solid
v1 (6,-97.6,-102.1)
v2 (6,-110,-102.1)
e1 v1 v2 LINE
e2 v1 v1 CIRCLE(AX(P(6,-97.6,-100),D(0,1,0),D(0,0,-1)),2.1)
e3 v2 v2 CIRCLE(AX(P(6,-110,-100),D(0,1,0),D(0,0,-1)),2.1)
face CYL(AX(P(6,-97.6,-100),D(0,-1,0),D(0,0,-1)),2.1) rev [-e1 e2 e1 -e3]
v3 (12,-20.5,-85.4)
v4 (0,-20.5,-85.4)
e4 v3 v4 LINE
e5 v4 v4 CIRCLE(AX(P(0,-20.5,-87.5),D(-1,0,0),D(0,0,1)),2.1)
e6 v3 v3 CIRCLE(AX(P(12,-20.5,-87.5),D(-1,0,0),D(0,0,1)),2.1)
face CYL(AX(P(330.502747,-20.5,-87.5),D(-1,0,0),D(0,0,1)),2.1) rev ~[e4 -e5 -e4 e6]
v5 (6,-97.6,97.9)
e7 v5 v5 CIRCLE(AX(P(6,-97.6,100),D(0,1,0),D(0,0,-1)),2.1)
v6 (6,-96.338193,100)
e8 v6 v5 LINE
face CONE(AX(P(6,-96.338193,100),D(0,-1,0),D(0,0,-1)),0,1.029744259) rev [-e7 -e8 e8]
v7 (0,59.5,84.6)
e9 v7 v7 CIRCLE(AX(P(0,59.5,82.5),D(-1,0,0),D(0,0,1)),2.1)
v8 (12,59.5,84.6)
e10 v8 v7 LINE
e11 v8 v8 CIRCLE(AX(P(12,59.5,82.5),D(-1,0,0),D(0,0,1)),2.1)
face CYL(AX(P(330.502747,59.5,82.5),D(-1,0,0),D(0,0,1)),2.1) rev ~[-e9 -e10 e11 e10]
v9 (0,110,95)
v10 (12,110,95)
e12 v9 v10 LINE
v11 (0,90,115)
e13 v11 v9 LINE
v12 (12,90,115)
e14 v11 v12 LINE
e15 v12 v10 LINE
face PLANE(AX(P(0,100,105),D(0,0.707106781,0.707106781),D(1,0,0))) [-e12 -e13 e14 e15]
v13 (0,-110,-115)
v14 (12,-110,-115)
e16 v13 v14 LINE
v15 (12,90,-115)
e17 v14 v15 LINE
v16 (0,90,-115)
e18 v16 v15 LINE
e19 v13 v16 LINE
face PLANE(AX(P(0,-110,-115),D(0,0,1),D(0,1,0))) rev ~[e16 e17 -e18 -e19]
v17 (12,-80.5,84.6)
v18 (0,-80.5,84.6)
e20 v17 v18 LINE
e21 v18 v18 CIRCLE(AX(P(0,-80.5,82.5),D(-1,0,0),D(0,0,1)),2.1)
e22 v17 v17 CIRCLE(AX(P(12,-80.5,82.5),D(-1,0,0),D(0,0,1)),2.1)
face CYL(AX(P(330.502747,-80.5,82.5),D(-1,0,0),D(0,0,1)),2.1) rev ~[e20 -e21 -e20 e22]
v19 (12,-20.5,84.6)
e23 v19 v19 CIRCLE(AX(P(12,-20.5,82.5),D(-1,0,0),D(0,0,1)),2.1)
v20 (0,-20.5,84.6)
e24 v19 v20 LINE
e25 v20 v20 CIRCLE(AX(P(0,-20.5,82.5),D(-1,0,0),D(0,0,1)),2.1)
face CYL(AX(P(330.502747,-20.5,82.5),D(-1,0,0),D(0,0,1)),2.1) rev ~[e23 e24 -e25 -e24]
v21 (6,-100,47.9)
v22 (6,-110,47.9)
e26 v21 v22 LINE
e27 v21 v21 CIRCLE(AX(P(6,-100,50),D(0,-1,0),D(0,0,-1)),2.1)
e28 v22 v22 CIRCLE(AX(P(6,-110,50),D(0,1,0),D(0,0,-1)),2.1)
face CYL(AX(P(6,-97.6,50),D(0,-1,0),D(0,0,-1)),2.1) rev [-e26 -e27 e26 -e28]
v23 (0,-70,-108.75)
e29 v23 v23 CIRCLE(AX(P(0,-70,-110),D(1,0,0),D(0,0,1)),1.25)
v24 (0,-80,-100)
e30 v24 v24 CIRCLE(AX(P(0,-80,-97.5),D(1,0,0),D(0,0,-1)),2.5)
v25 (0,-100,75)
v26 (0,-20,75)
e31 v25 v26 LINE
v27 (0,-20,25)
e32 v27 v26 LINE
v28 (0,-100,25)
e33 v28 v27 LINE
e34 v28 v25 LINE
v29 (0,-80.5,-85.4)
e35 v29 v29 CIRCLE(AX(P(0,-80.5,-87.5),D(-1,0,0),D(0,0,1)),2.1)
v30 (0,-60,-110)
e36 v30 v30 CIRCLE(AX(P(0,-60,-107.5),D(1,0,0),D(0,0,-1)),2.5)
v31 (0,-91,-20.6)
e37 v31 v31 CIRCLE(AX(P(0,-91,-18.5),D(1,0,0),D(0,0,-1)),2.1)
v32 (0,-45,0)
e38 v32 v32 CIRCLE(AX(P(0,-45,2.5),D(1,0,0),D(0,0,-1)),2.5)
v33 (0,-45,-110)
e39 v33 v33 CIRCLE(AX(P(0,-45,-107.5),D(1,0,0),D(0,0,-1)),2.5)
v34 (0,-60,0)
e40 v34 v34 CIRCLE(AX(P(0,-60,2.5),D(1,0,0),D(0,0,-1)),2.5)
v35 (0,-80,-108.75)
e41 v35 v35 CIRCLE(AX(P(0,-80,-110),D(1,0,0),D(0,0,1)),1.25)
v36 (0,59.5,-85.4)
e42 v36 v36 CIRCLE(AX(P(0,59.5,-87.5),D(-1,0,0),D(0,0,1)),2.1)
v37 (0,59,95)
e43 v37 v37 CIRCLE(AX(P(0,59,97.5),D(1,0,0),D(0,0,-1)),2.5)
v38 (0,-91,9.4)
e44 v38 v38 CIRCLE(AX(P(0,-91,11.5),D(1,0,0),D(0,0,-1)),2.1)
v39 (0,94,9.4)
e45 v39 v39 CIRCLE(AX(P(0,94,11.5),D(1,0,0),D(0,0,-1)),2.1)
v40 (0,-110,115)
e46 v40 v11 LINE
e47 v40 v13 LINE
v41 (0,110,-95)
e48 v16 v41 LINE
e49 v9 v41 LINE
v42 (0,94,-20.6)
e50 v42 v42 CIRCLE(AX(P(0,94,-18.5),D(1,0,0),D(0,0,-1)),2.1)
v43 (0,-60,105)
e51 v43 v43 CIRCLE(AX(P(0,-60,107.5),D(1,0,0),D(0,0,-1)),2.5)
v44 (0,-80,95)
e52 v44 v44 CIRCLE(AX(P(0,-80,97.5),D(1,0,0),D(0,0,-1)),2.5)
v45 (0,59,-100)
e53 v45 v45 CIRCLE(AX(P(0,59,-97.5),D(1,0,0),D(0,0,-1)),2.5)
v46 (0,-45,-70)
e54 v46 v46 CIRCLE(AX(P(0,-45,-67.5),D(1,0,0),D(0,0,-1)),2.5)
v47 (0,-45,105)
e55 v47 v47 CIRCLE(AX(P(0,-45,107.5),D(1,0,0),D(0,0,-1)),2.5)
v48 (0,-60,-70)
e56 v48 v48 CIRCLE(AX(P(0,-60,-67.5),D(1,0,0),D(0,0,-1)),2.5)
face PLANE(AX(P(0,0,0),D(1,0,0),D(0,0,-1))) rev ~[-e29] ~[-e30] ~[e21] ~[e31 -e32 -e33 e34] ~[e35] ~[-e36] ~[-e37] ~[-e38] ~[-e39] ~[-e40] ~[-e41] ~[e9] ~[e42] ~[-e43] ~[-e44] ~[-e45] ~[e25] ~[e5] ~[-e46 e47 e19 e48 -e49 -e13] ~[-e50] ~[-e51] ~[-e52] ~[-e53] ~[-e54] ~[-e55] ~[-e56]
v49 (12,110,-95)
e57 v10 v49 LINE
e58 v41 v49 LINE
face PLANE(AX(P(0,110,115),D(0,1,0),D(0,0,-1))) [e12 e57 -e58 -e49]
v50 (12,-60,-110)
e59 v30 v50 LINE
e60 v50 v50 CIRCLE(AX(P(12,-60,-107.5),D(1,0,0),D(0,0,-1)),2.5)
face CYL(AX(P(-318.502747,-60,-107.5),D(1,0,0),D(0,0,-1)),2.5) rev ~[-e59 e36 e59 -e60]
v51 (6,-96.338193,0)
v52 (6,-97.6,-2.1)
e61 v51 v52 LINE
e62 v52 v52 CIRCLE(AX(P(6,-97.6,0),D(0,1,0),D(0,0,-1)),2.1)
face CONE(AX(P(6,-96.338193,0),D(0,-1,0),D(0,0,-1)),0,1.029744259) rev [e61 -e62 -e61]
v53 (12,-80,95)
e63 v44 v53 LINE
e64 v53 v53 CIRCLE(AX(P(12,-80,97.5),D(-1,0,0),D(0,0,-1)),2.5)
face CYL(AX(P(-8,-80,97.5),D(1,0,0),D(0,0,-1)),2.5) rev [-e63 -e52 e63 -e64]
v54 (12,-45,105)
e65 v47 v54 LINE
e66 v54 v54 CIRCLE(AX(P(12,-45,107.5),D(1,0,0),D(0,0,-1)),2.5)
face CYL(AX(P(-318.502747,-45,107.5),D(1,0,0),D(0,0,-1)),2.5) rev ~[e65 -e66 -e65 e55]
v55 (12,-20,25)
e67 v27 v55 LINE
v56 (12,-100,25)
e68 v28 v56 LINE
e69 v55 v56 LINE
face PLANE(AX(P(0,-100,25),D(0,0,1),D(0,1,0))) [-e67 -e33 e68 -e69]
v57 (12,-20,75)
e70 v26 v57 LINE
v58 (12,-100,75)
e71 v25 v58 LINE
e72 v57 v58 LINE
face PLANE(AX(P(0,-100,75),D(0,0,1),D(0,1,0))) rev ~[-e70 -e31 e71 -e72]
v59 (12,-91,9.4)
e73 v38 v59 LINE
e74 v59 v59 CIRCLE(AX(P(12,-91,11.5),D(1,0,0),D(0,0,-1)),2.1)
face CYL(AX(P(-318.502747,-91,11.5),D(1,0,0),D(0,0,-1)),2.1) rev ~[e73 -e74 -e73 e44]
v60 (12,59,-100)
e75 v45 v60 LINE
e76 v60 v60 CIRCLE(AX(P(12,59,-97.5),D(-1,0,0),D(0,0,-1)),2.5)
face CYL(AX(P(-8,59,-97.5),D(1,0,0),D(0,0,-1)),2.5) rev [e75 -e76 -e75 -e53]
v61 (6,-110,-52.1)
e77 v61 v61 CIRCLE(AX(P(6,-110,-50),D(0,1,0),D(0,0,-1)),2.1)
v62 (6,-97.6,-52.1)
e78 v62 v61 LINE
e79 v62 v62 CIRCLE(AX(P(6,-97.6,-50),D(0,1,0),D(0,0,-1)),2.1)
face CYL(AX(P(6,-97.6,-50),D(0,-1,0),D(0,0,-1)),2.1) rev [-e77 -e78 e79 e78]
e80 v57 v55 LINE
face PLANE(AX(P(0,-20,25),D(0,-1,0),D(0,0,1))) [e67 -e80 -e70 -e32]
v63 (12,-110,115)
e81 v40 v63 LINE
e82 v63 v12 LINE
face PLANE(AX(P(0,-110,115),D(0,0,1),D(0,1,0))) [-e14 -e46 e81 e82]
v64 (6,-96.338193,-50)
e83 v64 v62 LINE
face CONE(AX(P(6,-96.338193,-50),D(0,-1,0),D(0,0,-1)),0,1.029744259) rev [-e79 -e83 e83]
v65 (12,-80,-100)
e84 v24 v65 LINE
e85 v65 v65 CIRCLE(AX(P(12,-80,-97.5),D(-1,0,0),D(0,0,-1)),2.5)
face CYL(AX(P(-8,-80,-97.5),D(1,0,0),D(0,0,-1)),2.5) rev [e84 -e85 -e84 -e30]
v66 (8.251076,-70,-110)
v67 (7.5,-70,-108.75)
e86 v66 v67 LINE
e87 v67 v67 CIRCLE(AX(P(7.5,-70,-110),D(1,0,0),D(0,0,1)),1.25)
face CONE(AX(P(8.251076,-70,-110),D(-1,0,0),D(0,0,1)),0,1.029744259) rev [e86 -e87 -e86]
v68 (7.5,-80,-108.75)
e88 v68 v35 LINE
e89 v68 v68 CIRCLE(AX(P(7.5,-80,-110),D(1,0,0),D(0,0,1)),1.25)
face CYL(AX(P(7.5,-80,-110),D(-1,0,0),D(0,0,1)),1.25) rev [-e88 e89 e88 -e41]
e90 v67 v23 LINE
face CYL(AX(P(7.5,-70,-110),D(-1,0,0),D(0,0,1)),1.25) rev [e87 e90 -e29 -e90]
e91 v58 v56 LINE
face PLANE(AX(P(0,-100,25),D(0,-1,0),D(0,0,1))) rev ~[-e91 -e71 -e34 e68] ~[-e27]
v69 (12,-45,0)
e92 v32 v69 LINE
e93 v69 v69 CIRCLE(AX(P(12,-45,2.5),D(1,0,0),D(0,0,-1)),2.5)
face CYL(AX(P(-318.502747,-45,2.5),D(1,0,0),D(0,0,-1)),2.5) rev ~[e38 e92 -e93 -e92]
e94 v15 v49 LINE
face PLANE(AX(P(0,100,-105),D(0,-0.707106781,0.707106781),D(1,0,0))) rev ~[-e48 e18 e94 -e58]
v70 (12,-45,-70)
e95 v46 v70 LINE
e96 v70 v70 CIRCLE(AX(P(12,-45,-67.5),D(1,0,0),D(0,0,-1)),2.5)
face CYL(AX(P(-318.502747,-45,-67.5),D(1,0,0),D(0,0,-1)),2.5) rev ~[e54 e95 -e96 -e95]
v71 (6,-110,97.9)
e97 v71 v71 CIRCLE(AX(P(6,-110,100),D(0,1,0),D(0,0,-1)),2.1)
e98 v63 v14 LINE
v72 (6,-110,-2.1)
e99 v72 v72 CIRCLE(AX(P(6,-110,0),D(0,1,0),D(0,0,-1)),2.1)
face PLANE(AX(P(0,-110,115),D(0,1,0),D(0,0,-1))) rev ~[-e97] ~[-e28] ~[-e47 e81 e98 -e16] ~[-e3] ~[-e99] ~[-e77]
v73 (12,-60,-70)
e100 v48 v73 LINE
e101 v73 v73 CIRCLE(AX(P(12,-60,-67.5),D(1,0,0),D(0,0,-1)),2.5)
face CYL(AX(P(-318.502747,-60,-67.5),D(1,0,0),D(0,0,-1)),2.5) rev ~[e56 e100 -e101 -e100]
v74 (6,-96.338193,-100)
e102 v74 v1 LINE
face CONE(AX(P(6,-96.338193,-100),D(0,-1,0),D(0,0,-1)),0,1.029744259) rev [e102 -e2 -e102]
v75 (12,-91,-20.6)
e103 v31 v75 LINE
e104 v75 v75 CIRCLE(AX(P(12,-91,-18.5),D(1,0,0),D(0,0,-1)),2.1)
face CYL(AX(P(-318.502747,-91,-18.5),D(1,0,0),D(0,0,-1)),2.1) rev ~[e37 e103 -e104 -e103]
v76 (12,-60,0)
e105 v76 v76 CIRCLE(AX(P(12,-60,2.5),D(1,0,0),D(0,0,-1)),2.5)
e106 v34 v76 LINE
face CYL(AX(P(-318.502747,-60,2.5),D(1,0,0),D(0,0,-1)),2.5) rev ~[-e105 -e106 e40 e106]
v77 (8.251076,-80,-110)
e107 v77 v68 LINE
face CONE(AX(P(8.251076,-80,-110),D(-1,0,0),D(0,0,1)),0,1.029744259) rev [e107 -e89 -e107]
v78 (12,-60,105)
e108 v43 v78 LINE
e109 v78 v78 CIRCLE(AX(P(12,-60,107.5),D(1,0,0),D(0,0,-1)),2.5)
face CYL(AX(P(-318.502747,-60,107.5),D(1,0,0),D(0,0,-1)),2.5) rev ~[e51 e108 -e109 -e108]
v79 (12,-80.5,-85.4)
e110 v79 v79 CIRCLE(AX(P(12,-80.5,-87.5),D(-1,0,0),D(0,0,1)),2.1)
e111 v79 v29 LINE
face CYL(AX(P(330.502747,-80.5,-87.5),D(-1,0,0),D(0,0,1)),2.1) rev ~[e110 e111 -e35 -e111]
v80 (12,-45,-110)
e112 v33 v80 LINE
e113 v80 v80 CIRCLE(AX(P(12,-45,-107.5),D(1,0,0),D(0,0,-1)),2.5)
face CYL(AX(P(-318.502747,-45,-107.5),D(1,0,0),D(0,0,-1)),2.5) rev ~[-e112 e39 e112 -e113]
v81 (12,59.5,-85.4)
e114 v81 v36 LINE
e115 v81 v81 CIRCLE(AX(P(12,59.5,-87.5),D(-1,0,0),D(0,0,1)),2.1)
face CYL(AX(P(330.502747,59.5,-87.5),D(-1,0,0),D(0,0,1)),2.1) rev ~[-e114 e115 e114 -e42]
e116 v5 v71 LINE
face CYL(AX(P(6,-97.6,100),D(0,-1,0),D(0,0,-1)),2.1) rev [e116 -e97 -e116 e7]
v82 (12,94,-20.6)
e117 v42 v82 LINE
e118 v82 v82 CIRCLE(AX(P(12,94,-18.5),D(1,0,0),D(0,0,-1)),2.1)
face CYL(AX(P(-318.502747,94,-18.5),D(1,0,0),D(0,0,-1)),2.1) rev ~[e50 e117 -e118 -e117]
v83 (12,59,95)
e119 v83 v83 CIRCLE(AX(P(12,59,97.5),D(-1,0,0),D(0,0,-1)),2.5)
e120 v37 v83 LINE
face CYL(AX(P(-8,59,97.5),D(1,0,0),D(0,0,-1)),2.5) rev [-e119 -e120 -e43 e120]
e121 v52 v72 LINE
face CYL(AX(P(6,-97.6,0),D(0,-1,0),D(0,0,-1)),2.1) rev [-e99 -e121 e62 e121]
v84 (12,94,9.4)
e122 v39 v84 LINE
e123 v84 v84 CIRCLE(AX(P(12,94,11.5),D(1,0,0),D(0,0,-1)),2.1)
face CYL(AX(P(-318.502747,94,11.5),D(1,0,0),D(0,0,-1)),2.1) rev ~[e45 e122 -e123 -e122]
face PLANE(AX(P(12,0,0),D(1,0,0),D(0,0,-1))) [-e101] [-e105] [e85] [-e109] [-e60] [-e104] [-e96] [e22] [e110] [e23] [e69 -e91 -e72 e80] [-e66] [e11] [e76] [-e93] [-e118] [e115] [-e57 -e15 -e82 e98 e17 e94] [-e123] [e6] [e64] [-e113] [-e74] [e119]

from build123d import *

# Parameters (mm, degrees)
SKETCH_1_W                  = 230
SKETCH_1_H                  = 220
BOSS_EXTRUDE_1_DEPTH        = 12
CHAMFER_1_SIZE              = 20
SKETCH_11_W                 = 50
SKETCH_11_H                 = 80
CUT_EXTRUDE_1_DEPTH         = 160.590099944
M6_TAPPED_HOLE_1_D          = 5
LINEAR_PATTERN_4_COUNT      = 2
LINEAR_PATTERN_4_PITCH      = 15
LINEAR_PATTERN_5_COUNT      = 3
LINEAR_PATTERN_5_PITCH      = 50
LINEAR_PATTERN_5_COL_COUNT  = 3
LINEAR_PATTERN_5_COL_PITCH  = 50
LINEAR_PATTERN_6_COUNT      = 2
LINEAR_PATTERN_6_PITCH      = 110
LINEAR_PATTERN_6_COPY_1_D   = 5
M5_TAPPED_HOLE_2_D          = 4.2
LINEAR_PATTERN_7_COUNT      = 2
LINEAR_PATTERN_7_PITCH      = 30
LINEAR_PATTERN_7_COUNT_DIR2 = 2
LINEAR_PATTERN_7_PITCH_DIR2 = 185
LINEAR_PATTERN_8_COUNT      = 2
LINEAR_PATTERN_8_PITCH      = 139
LINEAR_PATTERN_9_COUNT      = 2
LINEAR_PATTERN_9_PITCH      = 195
M5_TAPPED_HOLE_3_D          = 4.2
LINEAR_PATTERN_10_COUNT     = 2
LINEAR_PATTERN_10_PITCH     = 60
LINEAR_PATTERN_11_COUNT     = 2
LINEAR_PATTERN_11_PITCH     = 140
LINEAR_PATTERN_12_COUNT     = 2
LINEAR_PATTERN_12_PITCH     = 170
LINEAR_PATTERN_12_COPY_1_D  = 4.2
LINEAR_PATTERN_12_COPY_2_D  = 4.2
LINEAR_PATTERN_13_COUNT     = 2
LINEAR_PATTERN_13_PITCH     = 215
LINEAR_PATTERN_13_COPY_1_D  = 5
LINEAR_PATTERN_14_COUNT     = 2
LINEAR_PATTERN_14_PITCH     = 40
LINEAR_PATTERN_14_COPY_1_D  = 5
LINEAR_PATTERN_15_COUNT     = 2
LINEAR_PATTERN_15_PITCH     = 10


with BuildPart() as part:
    # Sketch 1 → Boss-Extrude 1 (new body)
    with BuildSketch(Plane(origin=(0, 0, 0), x_dir=(0, 0, -1), z_dir=(1, 0, 0))):
        Rectangle(SKETCH_1_W, SKETCH_1_H)
    extrude(amount=BOSS_EXTRUDE_1_DEPTH)

    # Chamfer 1
    chamfer_1_edges = [part.edges().sort_by_distance(p)[0] for p in [
        (6, 110, 115),
        (6, 110, -115),
    ]]
    chamfer(chamfer_1_edges, length=CHAMFER_1_SIZE)

    # Sketch 11 → Cut-Extrude 1 (cut, through all)
    with BuildSketch(Plane.ZY):
        with Locations((50, -60)):
            Rectangle(SKETCH_11_W, SKETCH_11_H)
    extrude(amount=-CUT_EXTRUDE_1_DEPTH, mode=Mode.SUBTRACT)

    # M6 Tapped Hole 1 (through all)
    with Locations(Plane.ZY):
        with Locations((-107.5, -60)):
            m6_tapped_hole_1 = Hole(M6_TAPPED_HOLE_1_D / 2)

    # Linear Pattern 4: M6 Tapped Hole 1 ×2
    with Locations(*[(0, i * LINEAR_PATTERN_4_PITCH, 0) for i in range(1, LINEAR_PATTERN_4_COUNT)]):
        add(m6_tapped_hole_1, mode=Mode.SUBTRACT)

    # Sketch 14 → M5 Tapped Hole 1 (revolve, cut)
    with BuildSketch(Plane(origin=(6, -110, 0), x_dir=(0, 0, -1), z_dir=(1, 0, 0))):
        Polygon((0, 0), (0, 13.6618073), (2.1, 12.4), (2.1, 0), align=None)
    m5_tapped_hole_1 = revolve(axis=Axis((6, -116.35, 0), (0, 1, 0)), mode=Mode.SUBTRACT)

    # Linear Pattern 5: M5 Tapped Hole 1 ×3
    with Locations(*[(0, 0, -i * LINEAR_PATTERN_5_PITCH) for i in range(1, LINEAR_PATTERN_5_COUNT)]):
        add(m5_tapped_hole_1, mode=Mode.SUBTRACT)

    # Linear Pattern 5 col: M5 Tapped Hole 1 ×3
    with Locations(*[(0, 0, i * LINEAR_PATTERN_5_COL_PITCH) for i in range(1, LINEAR_PATTERN_5_COL_COUNT)]):
        add(m5_tapped_hole_1, mode=Mode.SUBTRACT)

    # Linear Pattern 6: M6 Tapped Hole 1 ×2
    with Locations(*[(0, 0, i * LINEAR_PATTERN_6_PITCH) for i in range(1, LINEAR_PATTERN_6_COUNT)]):
        add(m6_tapped_hole_1, mode=Mode.SUBTRACT)

    # Linear Pattern 6 copy 1 (through all)
    with Locations(Plane(origin=(0, 15, 110), x_dir=(0, 0, 1), z_dir=(-1, 0, 0))):
        with Locations((-107.5, -60)):
            Hole(LINEAR_PATTERN_6_COPY_1_D / 2)

    # M5 Tapped Hole 2 (through all)
    with Locations(Plane.ZY):
        with Locations((11.5, -91)):
            m5_tapped_hole_2 = Hole(M5_TAPPED_HOLE_2_D / 2)

    # Linear Pattern 7: M5 Tapped Hole 2 2 × 2
    with Locations(*[(0, j * LINEAR_PATTERN_7_PITCH_DIR2, -i * LINEAR_PATTERN_7_PITCH) for i in range(LINEAR_PATTERN_7_COUNT) for j in range(LINEAR_PATTERN_7_COUNT_DIR2) if (i, j) != (0, 0)]):
        add(m5_tapped_hole_2, mode=Mode.SUBTRACT)

    # Sketch 18 → Ø5.0 (5) Hole 1 (revolve, cut)
    with BuildSketch(Plane(origin=(12, -80, 97.5), x_dir=(0, 0, -1), z_dir=(0, 1, 0))):
        Polygon((0, 0), (0, 21.502151548), (2.5, 20), (2.5, 0), align=None)
    f_5_0_5_hole_1 = revolve(axis=Axis((18.35, -80, 97.5), (-1, 0, 0)), mode=Mode.SUBTRACT)

    # Linear Pattern 8: Ø5.0 (5) Hole 1 ×2
    with Locations(*[(0, i * LINEAR_PATTERN_8_PITCH, 0) for i in range(1, LINEAR_PATTERN_8_COUNT)]):
        add(f_5_0_5_hole_1, mode=Mode.SUBTRACT)

    # Linear Pattern 9: Ø5.0 (5) Hole 1 ×2
    with Locations(*[(0, 0, -i * LINEAR_PATTERN_9_PITCH) for i in range(1, LINEAR_PATTERN_9_COUNT)]):
        add(f_5_0_5_hole_1, mode=Mode.SUBTRACT)

    # Linear Pattern 9 copy 1 sketch → Linear Pattern 9 copy 1 (revolve, cut)
    with BuildSketch(Plane(origin=(12, 59, -97.5), x_dir=(0, 0, -1), z_dir=(0, 1, 0))):
        Polygon((0, 0), (0, 21.502151548), (2.5, 20), (2.5, 0), align=None)
    revolve(axis=Axis((18.35, 59, -97.5), (-1, 0, 0)), mode=Mode.SUBTRACT)

    # M5 Tapped Hole 3 (through all)
    with Locations(Plane(origin=(12, 0, 0), x_dir=(0, 0, -1), z_dir=(1, 0, 0))):
        with Locations((-82.5, -80.5)):
            m5_tapped_hole_3 = Hole(M5_TAPPED_HOLE_3_D / 2)

    # Linear Pattern 10: M5 Tapped Hole 3 ×2
    with Locations(*[(0, i * LINEAR_PATTERN_10_PITCH, 0) for i in range(1, LINEAR_PATTERN_10_COUNT)]):
        add(m5_tapped_hole_3, mode=Mode.SUBTRACT)

    # Linear Pattern 11: M5 Tapped Hole 3 ×2
    with Locations(*[(0, i * LINEAR_PATTERN_11_PITCH, 0) for i in range(1, LINEAR_PATTERN_11_COUNT)]):
        add(m5_tapped_hole_3, mode=Mode.SUBTRACT)

    # Linear Pattern 12: M5 Tapped Hole 3 ×2
    with Locations(*[(0, 0, -i * LINEAR_PATTERN_12_PITCH) for i in range(1, LINEAR_PATTERN_12_COUNT)]):
        add(m5_tapped_hole_3, mode=Mode.SUBTRACT)

    # Linear Pattern 12 copy 1 (through all)
    with Locations(Plane(origin=(12, 60, -170), x_dir=(0, 0, -1), z_dir=(1, 0, 0))):
        with Locations((-82.5, -80.5)):
            Hole(LINEAR_PATTERN_12_COPY_1_D / 2)

    # Linear Pattern 12 copy 2 (through all)
    with Locations(Plane(origin=(12, 140, -170), x_dir=(0, 0, -1), z_dir=(1, 0, 0))):
        with Locations((-82.5, -80.5)):
            Hole(LINEAR_PATTERN_12_COPY_2_D / 2)

    # Linear Pattern 13: M6 Tapped Hole 1 ×2
    with Locations(*[(0, 0, i * LINEAR_PATTERN_13_PITCH) for i in range(1, LINEAR_PATTERN_13_COUNT)]):
        add(m6_tapped_hole_1, mode=Mode.SUBTRACT)

    # Linear Pattern 13 copy 1 (through all)
    with Locations(Plane(origin=(0, 15, 215), x_dir=(0, 0, 1), z_dir=(-1, 0, 0))):
        with Locations((-107.5, -60)):
            Hole(LINEAR_PATTERN_13_COPY_1_D / 2)

    # Linear Pattern 14: M6 Tapped Hole 1 ×2
    with Locations(*[(0, 0, i * LINEAR_PATTERN_14_PITCH) for i in range(1, LINEAR_PATTERN_14_COUNT)]):
        add(m6_tapped_hole_1, mode=Mode.SUBTRACT)

    # Linear Pattern 14 copy 1 (through all)
    with Locations(Plane(origin=(0, 15, 40), x_dir=(0, 0, 1), z_dir=(-1, 0, 0))):
        with Locations((-107.5, -60)):
            Hole(LINEAR_PATTERN_14_COPY_1_D / 2)

    # Sketch 22 → M3 Tapped Hole 1 (revolve, cut)
    with BuildSketch(Plane(origin=(0, -70, -110), x_dir=(0, 0, 1), z_dir=(0, 1, 0))):
        Polygon((0, 0), (0, 8.251075774), (1.25, 7.5), (1.25, 0), align=None)
    m3_tapped_hole_1 = revolve(axis=Axis((-6.35, -70, -110), (1, 0, 0)), mode=Mode.SUBTRACT)

    # Linear Pattern 15: M3 Tapped Hole 1 ×2
    with Locations(*[(0, -i * LINEAR_PATTERN_15_PITCH, 0) for i in range(1, LINEAR_PATTERN_15_COUNT)]):
        add(m3_tapped_hole_1, mode=Mode.SUBTRACT)


solid = part.part
